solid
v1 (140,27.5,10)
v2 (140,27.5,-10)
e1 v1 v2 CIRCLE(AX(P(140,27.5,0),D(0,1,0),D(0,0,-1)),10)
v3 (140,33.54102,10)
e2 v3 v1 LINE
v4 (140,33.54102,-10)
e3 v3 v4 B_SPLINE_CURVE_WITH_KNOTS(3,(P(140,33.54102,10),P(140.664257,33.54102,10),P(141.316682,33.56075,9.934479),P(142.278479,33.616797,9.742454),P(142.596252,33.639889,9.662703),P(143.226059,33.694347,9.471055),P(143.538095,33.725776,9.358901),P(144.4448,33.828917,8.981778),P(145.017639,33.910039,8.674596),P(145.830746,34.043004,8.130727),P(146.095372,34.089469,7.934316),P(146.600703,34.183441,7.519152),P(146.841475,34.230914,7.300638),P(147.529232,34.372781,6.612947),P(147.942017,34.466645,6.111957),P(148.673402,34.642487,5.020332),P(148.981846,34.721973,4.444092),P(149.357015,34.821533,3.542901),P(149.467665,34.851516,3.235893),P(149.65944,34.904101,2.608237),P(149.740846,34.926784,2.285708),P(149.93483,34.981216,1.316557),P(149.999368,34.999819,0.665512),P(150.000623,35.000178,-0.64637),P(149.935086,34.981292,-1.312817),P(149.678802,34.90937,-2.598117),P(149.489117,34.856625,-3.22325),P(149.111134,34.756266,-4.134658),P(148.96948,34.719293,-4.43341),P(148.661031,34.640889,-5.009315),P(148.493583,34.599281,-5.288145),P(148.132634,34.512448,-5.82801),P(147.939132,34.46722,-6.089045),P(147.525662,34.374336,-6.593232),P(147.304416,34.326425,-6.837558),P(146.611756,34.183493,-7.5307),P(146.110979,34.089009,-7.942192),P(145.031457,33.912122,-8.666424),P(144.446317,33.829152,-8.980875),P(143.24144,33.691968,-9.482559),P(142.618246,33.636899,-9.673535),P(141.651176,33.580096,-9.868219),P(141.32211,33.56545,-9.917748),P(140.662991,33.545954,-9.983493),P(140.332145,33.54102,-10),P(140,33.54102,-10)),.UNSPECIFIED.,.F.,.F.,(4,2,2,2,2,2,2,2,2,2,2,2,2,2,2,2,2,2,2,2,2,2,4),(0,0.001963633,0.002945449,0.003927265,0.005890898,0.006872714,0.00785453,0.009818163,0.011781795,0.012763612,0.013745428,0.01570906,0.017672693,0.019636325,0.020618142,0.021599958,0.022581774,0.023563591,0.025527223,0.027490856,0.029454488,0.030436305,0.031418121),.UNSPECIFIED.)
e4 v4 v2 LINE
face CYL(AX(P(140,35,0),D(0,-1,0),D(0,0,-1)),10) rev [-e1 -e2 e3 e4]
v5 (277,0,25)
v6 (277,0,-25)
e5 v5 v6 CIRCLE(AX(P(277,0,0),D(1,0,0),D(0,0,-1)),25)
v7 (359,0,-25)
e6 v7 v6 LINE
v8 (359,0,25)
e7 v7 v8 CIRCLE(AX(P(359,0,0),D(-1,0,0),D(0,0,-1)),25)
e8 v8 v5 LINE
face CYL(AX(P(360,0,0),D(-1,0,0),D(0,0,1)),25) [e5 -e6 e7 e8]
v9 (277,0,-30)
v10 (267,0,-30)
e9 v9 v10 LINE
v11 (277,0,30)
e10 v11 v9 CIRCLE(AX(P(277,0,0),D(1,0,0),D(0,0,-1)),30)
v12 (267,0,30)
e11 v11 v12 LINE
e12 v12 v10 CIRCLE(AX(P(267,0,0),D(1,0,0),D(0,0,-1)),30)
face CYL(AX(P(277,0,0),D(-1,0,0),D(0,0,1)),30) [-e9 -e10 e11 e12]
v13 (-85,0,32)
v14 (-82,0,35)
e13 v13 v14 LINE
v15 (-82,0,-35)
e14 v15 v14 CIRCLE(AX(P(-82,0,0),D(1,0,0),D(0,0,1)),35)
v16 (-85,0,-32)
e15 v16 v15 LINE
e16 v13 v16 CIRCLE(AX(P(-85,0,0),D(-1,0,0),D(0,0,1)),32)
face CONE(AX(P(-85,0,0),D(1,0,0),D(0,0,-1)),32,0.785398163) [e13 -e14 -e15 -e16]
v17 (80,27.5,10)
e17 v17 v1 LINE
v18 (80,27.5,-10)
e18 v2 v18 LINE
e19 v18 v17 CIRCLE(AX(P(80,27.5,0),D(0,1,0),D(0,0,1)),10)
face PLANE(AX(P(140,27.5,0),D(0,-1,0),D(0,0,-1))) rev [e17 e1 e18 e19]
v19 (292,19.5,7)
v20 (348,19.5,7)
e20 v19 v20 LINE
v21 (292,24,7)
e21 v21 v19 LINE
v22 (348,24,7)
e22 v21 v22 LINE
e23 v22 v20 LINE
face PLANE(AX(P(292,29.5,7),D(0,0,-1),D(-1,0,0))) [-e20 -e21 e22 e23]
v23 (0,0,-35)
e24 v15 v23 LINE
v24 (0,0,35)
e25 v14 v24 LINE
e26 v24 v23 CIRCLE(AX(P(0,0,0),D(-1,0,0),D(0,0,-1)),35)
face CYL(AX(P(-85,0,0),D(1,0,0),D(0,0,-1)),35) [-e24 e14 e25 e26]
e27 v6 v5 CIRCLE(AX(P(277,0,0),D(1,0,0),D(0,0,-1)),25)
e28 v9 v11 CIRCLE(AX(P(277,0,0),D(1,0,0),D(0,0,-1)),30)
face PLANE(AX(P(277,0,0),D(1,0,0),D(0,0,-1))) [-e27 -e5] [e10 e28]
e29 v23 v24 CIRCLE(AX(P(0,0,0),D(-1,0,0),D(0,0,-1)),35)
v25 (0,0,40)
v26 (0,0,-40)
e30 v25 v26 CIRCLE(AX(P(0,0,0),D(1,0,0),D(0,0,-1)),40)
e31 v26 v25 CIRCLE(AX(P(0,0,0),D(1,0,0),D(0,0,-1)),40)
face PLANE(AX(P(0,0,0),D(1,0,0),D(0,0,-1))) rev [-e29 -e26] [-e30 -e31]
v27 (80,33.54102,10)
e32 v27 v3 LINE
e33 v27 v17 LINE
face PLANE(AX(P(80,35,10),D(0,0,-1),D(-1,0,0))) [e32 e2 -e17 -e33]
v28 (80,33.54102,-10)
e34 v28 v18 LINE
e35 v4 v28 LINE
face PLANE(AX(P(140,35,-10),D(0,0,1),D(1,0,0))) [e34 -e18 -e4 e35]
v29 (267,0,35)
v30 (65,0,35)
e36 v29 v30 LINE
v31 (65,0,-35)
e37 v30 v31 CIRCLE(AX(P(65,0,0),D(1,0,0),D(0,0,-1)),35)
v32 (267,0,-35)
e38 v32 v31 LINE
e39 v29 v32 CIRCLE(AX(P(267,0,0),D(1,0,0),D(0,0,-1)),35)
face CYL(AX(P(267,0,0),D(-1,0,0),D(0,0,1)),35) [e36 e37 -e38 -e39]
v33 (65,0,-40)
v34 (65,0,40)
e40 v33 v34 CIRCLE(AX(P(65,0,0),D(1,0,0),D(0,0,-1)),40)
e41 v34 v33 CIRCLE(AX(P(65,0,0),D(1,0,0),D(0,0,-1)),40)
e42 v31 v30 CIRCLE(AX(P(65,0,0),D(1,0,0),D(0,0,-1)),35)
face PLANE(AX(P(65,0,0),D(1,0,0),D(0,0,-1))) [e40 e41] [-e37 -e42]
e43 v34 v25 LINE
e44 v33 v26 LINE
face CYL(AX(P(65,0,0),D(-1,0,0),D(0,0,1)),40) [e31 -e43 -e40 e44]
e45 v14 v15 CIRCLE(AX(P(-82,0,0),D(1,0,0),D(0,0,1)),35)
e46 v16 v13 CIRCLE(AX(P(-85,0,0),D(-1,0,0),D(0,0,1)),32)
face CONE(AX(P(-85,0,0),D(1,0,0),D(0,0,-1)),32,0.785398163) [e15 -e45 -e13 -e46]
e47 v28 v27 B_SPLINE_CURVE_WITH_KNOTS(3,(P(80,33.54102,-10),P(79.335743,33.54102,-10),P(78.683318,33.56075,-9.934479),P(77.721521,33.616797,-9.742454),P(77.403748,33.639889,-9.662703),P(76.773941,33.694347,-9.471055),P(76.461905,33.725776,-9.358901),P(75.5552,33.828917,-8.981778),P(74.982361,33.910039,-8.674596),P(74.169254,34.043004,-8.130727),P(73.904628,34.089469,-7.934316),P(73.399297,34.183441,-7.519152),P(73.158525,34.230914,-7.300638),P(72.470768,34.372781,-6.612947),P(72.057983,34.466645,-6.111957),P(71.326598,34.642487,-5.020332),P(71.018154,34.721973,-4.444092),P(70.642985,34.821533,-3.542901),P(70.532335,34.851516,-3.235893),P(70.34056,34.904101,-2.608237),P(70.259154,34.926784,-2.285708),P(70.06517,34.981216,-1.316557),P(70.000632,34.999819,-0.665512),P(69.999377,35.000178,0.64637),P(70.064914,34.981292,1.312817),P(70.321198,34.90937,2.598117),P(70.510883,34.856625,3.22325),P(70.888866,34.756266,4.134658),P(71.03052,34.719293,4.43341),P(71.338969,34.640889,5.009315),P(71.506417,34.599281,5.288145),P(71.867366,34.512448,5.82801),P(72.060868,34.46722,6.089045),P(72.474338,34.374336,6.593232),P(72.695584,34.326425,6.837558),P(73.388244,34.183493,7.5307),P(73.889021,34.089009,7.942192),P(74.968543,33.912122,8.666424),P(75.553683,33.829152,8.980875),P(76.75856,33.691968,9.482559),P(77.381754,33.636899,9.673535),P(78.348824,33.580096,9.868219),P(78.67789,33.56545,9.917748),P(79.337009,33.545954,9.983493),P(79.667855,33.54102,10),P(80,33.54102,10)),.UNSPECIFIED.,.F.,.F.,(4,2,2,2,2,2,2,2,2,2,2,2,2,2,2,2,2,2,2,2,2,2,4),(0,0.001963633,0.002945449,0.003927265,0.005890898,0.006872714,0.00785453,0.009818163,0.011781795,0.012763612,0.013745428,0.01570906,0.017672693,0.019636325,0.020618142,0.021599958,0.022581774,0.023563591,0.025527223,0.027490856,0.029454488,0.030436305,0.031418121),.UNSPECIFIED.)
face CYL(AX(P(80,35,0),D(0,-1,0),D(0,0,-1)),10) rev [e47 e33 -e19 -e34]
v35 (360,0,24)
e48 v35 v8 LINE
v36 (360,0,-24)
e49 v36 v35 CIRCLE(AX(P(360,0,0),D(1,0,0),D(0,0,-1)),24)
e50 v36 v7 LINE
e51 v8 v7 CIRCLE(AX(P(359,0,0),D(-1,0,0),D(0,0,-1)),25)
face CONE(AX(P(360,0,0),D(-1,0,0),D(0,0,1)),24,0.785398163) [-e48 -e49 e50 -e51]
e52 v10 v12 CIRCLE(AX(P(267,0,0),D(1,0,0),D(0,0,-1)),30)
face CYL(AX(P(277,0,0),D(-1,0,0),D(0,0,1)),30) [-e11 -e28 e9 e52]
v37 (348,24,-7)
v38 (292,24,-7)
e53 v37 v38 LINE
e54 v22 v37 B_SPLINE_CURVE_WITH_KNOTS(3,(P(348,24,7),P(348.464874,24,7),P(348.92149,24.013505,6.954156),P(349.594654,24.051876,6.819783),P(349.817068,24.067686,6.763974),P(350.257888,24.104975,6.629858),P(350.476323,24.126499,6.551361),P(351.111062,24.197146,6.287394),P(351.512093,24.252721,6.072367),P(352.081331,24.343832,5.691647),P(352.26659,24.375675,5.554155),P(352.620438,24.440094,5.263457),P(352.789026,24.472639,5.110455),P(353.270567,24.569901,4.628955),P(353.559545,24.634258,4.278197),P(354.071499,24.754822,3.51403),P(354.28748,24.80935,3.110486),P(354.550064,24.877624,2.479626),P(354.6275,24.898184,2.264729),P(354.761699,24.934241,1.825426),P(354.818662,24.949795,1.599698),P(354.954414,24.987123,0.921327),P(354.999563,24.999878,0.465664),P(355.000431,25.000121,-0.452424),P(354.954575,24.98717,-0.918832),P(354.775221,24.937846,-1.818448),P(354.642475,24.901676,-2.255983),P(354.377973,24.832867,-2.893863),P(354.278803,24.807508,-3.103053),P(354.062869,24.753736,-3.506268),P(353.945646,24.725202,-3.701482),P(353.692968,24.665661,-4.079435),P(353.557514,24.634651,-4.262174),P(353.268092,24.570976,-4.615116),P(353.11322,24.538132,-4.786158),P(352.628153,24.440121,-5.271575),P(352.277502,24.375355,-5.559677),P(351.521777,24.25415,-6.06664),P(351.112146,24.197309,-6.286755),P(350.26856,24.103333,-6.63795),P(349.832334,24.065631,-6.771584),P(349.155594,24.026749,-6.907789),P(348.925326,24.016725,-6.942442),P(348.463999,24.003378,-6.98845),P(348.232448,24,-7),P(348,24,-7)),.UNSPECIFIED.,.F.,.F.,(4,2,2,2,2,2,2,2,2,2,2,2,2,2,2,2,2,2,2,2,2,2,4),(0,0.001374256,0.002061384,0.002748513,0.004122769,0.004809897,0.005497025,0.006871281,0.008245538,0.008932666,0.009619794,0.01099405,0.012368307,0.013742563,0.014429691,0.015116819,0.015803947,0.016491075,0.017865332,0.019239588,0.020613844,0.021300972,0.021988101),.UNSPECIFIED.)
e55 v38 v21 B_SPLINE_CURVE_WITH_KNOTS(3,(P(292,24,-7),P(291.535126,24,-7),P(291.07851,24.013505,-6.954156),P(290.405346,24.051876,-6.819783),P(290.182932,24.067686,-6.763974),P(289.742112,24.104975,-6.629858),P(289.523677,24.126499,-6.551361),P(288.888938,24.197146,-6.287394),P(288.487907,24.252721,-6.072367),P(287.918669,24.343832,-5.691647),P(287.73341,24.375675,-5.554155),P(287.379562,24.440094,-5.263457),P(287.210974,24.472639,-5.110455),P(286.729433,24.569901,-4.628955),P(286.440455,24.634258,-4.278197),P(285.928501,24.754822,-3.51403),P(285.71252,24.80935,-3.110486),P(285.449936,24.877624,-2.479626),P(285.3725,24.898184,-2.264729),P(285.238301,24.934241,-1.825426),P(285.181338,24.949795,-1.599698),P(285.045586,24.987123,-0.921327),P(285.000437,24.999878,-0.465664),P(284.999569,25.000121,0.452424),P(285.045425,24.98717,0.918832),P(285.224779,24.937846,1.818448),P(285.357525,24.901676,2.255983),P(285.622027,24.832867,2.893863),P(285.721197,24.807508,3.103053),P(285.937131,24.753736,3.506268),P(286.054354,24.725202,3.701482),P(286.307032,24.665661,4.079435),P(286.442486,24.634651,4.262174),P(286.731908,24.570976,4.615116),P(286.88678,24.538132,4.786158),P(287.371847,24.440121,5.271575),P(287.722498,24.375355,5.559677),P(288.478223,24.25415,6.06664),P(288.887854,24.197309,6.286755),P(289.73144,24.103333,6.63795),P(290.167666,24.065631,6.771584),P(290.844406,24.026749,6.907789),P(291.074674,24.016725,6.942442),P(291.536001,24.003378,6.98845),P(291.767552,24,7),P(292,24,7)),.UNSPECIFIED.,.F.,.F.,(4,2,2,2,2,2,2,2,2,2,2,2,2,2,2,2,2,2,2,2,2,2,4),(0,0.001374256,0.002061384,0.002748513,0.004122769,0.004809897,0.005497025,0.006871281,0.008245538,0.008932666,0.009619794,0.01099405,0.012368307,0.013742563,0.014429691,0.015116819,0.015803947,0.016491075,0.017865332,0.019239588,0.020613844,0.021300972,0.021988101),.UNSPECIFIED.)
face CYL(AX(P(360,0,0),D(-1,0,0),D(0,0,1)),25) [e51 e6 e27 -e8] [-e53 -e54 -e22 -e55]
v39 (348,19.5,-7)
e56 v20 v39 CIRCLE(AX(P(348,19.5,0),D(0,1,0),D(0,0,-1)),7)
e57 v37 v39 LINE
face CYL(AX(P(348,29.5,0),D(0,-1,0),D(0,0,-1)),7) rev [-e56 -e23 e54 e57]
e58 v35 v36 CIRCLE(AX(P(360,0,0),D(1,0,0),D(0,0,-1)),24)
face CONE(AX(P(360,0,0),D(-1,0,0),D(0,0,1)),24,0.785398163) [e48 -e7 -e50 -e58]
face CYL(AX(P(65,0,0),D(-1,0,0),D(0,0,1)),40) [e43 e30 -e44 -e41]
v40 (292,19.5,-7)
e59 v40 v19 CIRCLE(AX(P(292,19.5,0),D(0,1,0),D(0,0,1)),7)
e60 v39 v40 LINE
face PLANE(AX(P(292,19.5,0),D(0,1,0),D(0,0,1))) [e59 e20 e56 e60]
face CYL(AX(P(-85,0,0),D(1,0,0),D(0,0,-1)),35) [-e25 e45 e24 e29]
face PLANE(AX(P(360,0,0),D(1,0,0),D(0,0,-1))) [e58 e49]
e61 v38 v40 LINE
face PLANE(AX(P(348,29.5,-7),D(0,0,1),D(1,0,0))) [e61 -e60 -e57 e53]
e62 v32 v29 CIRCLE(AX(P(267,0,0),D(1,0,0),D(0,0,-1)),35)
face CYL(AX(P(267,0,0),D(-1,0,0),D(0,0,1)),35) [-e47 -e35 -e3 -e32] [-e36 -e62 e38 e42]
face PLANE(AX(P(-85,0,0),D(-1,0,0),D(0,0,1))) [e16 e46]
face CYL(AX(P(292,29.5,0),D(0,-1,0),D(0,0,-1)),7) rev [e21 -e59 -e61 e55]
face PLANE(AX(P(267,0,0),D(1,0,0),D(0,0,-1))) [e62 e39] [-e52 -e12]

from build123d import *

# Parameters (mm, degrees)
SKETCH1_R      = 40
EXTRUDE1_DEPTH = 65
SKETCH2_R      = 35
EXTRUDE2_DEPTH = 202
EXTRUDE3_START = 85
SKETCH3_R      = 35
EXTRUDE3_DEPTH = 85
CHAMFER1_SIZE  = 3
EXTRUDE4_DEPTH = 7.5
SKETCH5_R      = 30
EXTRUDE5_DEPTH = 10
SKETCH7_R      = 25
EXTRUDE6_DEPTH = 83
EXTRUDE7_DEPTH = 10
CHAMFER2_SIZE  = 1


with BuildPart() as part:
    # Sketch1 → Extrude1 (new body)
    with BuildSketch(Plane(origin=(0, 0, 0), x_dir=(0, 0, -1), z_dir=(1, 0, 0))):
        Circle(SKETCH1_R)
    extrude(amount=EXTRUDE1_DEPTH)

    # Sketch2 → Extrude2 (add)
    with BuildSketch(Plane(origin=(65, 0, 0), x_dir=(0, 0, -1), z_dir=(1, 0, 0))):
        Circle(SKETCH2_R)
    extrude(amount=EXTRUDE2_DEPTH)

    # Sketch3 → Extrude3 (add)
    with BuildSketch(Plane.ZY.offset(EXTRUDE3_START)):
        with Locations(Location((0, 0, 0), (0, 0, 180))):
            Circle(SKETCH3_R)
    extrude(amount=-EXTRUDE3_DEPTH)

    # Chamfer1
    chamfer1_edges = [part.edges().sort_by_distance(p)[0] for p in [
        (-85, 0, 35),
    ]]
    chamfer(chamfer1_edges, length=CHAMFER1_SIZE)

    # Sketch4 → Extrude4 (cut)
    with BuildSketch(Plane(origin=(0, 27.5, 0), x_dir=(-1, 0, 0), z_dir=(0, 1, 0))):
        with BuildLine():
            Line((-80, 10), (-140, 10))
            ThreePointArc((-140, 10), (-150, 0), (-140, -10))
            Line((-140, -10), (-80, -10))
            ThreePointArc((-80, -10), (-70, 0), (-80, 10))
        make_face()
    extrude(amount=EXTRUDE4_DEPTH, mode=Mode.SUBTRACT)

    # Sketch5 → Extrude5 (add)
    with BuildSketch(Plane(origin=(267, 0, 0), x_dir=(0, 0, -1), z_dir=(1, 0, 0))):
        Circle(SKETCH5_R)
    extrude(amount=EXTRUDE5_DEPTH)

    # Sketch7 → Extrude6 (add)
    with BuildSketch(Plane(origin=(277, 0, 0), x_dir=(0, 0, -1), z_dir=(1, 0, 0))):
        Circle(SKETCH7_R)
    extrude(amount=EXTRUDE6_DEPTH)

    # Sketch8 → Extrude7 (cut)
    with BuildSketch(Plane(origin=(0, 19.5, 0), x_dir=(-1, 0, 0), z_dir=(0, 1, 0))):
        with BuildLine():
            Line((-292, 7), (-348, 7))
            ThreePointArc((-348, 7), (-355, 0), (-348, -7))
            Line((-348, -7), (-292, -7))
            ThreePointArc((-292, -7), (-285, 0), (-292, 7))
        make_face()
    extrude(amount=EXTRUDE7_DEPTH, mode=Mode.SUBTRACT)

    # Chamfer2
    chamfer2_edges = [part.edges().sort_by_distance(p)[0] for p in [
        (360, 0, 25),
    ]]
    chamfer(chamfer2_edges, length=CHAMFER2_SIZE)


solid = part.part
